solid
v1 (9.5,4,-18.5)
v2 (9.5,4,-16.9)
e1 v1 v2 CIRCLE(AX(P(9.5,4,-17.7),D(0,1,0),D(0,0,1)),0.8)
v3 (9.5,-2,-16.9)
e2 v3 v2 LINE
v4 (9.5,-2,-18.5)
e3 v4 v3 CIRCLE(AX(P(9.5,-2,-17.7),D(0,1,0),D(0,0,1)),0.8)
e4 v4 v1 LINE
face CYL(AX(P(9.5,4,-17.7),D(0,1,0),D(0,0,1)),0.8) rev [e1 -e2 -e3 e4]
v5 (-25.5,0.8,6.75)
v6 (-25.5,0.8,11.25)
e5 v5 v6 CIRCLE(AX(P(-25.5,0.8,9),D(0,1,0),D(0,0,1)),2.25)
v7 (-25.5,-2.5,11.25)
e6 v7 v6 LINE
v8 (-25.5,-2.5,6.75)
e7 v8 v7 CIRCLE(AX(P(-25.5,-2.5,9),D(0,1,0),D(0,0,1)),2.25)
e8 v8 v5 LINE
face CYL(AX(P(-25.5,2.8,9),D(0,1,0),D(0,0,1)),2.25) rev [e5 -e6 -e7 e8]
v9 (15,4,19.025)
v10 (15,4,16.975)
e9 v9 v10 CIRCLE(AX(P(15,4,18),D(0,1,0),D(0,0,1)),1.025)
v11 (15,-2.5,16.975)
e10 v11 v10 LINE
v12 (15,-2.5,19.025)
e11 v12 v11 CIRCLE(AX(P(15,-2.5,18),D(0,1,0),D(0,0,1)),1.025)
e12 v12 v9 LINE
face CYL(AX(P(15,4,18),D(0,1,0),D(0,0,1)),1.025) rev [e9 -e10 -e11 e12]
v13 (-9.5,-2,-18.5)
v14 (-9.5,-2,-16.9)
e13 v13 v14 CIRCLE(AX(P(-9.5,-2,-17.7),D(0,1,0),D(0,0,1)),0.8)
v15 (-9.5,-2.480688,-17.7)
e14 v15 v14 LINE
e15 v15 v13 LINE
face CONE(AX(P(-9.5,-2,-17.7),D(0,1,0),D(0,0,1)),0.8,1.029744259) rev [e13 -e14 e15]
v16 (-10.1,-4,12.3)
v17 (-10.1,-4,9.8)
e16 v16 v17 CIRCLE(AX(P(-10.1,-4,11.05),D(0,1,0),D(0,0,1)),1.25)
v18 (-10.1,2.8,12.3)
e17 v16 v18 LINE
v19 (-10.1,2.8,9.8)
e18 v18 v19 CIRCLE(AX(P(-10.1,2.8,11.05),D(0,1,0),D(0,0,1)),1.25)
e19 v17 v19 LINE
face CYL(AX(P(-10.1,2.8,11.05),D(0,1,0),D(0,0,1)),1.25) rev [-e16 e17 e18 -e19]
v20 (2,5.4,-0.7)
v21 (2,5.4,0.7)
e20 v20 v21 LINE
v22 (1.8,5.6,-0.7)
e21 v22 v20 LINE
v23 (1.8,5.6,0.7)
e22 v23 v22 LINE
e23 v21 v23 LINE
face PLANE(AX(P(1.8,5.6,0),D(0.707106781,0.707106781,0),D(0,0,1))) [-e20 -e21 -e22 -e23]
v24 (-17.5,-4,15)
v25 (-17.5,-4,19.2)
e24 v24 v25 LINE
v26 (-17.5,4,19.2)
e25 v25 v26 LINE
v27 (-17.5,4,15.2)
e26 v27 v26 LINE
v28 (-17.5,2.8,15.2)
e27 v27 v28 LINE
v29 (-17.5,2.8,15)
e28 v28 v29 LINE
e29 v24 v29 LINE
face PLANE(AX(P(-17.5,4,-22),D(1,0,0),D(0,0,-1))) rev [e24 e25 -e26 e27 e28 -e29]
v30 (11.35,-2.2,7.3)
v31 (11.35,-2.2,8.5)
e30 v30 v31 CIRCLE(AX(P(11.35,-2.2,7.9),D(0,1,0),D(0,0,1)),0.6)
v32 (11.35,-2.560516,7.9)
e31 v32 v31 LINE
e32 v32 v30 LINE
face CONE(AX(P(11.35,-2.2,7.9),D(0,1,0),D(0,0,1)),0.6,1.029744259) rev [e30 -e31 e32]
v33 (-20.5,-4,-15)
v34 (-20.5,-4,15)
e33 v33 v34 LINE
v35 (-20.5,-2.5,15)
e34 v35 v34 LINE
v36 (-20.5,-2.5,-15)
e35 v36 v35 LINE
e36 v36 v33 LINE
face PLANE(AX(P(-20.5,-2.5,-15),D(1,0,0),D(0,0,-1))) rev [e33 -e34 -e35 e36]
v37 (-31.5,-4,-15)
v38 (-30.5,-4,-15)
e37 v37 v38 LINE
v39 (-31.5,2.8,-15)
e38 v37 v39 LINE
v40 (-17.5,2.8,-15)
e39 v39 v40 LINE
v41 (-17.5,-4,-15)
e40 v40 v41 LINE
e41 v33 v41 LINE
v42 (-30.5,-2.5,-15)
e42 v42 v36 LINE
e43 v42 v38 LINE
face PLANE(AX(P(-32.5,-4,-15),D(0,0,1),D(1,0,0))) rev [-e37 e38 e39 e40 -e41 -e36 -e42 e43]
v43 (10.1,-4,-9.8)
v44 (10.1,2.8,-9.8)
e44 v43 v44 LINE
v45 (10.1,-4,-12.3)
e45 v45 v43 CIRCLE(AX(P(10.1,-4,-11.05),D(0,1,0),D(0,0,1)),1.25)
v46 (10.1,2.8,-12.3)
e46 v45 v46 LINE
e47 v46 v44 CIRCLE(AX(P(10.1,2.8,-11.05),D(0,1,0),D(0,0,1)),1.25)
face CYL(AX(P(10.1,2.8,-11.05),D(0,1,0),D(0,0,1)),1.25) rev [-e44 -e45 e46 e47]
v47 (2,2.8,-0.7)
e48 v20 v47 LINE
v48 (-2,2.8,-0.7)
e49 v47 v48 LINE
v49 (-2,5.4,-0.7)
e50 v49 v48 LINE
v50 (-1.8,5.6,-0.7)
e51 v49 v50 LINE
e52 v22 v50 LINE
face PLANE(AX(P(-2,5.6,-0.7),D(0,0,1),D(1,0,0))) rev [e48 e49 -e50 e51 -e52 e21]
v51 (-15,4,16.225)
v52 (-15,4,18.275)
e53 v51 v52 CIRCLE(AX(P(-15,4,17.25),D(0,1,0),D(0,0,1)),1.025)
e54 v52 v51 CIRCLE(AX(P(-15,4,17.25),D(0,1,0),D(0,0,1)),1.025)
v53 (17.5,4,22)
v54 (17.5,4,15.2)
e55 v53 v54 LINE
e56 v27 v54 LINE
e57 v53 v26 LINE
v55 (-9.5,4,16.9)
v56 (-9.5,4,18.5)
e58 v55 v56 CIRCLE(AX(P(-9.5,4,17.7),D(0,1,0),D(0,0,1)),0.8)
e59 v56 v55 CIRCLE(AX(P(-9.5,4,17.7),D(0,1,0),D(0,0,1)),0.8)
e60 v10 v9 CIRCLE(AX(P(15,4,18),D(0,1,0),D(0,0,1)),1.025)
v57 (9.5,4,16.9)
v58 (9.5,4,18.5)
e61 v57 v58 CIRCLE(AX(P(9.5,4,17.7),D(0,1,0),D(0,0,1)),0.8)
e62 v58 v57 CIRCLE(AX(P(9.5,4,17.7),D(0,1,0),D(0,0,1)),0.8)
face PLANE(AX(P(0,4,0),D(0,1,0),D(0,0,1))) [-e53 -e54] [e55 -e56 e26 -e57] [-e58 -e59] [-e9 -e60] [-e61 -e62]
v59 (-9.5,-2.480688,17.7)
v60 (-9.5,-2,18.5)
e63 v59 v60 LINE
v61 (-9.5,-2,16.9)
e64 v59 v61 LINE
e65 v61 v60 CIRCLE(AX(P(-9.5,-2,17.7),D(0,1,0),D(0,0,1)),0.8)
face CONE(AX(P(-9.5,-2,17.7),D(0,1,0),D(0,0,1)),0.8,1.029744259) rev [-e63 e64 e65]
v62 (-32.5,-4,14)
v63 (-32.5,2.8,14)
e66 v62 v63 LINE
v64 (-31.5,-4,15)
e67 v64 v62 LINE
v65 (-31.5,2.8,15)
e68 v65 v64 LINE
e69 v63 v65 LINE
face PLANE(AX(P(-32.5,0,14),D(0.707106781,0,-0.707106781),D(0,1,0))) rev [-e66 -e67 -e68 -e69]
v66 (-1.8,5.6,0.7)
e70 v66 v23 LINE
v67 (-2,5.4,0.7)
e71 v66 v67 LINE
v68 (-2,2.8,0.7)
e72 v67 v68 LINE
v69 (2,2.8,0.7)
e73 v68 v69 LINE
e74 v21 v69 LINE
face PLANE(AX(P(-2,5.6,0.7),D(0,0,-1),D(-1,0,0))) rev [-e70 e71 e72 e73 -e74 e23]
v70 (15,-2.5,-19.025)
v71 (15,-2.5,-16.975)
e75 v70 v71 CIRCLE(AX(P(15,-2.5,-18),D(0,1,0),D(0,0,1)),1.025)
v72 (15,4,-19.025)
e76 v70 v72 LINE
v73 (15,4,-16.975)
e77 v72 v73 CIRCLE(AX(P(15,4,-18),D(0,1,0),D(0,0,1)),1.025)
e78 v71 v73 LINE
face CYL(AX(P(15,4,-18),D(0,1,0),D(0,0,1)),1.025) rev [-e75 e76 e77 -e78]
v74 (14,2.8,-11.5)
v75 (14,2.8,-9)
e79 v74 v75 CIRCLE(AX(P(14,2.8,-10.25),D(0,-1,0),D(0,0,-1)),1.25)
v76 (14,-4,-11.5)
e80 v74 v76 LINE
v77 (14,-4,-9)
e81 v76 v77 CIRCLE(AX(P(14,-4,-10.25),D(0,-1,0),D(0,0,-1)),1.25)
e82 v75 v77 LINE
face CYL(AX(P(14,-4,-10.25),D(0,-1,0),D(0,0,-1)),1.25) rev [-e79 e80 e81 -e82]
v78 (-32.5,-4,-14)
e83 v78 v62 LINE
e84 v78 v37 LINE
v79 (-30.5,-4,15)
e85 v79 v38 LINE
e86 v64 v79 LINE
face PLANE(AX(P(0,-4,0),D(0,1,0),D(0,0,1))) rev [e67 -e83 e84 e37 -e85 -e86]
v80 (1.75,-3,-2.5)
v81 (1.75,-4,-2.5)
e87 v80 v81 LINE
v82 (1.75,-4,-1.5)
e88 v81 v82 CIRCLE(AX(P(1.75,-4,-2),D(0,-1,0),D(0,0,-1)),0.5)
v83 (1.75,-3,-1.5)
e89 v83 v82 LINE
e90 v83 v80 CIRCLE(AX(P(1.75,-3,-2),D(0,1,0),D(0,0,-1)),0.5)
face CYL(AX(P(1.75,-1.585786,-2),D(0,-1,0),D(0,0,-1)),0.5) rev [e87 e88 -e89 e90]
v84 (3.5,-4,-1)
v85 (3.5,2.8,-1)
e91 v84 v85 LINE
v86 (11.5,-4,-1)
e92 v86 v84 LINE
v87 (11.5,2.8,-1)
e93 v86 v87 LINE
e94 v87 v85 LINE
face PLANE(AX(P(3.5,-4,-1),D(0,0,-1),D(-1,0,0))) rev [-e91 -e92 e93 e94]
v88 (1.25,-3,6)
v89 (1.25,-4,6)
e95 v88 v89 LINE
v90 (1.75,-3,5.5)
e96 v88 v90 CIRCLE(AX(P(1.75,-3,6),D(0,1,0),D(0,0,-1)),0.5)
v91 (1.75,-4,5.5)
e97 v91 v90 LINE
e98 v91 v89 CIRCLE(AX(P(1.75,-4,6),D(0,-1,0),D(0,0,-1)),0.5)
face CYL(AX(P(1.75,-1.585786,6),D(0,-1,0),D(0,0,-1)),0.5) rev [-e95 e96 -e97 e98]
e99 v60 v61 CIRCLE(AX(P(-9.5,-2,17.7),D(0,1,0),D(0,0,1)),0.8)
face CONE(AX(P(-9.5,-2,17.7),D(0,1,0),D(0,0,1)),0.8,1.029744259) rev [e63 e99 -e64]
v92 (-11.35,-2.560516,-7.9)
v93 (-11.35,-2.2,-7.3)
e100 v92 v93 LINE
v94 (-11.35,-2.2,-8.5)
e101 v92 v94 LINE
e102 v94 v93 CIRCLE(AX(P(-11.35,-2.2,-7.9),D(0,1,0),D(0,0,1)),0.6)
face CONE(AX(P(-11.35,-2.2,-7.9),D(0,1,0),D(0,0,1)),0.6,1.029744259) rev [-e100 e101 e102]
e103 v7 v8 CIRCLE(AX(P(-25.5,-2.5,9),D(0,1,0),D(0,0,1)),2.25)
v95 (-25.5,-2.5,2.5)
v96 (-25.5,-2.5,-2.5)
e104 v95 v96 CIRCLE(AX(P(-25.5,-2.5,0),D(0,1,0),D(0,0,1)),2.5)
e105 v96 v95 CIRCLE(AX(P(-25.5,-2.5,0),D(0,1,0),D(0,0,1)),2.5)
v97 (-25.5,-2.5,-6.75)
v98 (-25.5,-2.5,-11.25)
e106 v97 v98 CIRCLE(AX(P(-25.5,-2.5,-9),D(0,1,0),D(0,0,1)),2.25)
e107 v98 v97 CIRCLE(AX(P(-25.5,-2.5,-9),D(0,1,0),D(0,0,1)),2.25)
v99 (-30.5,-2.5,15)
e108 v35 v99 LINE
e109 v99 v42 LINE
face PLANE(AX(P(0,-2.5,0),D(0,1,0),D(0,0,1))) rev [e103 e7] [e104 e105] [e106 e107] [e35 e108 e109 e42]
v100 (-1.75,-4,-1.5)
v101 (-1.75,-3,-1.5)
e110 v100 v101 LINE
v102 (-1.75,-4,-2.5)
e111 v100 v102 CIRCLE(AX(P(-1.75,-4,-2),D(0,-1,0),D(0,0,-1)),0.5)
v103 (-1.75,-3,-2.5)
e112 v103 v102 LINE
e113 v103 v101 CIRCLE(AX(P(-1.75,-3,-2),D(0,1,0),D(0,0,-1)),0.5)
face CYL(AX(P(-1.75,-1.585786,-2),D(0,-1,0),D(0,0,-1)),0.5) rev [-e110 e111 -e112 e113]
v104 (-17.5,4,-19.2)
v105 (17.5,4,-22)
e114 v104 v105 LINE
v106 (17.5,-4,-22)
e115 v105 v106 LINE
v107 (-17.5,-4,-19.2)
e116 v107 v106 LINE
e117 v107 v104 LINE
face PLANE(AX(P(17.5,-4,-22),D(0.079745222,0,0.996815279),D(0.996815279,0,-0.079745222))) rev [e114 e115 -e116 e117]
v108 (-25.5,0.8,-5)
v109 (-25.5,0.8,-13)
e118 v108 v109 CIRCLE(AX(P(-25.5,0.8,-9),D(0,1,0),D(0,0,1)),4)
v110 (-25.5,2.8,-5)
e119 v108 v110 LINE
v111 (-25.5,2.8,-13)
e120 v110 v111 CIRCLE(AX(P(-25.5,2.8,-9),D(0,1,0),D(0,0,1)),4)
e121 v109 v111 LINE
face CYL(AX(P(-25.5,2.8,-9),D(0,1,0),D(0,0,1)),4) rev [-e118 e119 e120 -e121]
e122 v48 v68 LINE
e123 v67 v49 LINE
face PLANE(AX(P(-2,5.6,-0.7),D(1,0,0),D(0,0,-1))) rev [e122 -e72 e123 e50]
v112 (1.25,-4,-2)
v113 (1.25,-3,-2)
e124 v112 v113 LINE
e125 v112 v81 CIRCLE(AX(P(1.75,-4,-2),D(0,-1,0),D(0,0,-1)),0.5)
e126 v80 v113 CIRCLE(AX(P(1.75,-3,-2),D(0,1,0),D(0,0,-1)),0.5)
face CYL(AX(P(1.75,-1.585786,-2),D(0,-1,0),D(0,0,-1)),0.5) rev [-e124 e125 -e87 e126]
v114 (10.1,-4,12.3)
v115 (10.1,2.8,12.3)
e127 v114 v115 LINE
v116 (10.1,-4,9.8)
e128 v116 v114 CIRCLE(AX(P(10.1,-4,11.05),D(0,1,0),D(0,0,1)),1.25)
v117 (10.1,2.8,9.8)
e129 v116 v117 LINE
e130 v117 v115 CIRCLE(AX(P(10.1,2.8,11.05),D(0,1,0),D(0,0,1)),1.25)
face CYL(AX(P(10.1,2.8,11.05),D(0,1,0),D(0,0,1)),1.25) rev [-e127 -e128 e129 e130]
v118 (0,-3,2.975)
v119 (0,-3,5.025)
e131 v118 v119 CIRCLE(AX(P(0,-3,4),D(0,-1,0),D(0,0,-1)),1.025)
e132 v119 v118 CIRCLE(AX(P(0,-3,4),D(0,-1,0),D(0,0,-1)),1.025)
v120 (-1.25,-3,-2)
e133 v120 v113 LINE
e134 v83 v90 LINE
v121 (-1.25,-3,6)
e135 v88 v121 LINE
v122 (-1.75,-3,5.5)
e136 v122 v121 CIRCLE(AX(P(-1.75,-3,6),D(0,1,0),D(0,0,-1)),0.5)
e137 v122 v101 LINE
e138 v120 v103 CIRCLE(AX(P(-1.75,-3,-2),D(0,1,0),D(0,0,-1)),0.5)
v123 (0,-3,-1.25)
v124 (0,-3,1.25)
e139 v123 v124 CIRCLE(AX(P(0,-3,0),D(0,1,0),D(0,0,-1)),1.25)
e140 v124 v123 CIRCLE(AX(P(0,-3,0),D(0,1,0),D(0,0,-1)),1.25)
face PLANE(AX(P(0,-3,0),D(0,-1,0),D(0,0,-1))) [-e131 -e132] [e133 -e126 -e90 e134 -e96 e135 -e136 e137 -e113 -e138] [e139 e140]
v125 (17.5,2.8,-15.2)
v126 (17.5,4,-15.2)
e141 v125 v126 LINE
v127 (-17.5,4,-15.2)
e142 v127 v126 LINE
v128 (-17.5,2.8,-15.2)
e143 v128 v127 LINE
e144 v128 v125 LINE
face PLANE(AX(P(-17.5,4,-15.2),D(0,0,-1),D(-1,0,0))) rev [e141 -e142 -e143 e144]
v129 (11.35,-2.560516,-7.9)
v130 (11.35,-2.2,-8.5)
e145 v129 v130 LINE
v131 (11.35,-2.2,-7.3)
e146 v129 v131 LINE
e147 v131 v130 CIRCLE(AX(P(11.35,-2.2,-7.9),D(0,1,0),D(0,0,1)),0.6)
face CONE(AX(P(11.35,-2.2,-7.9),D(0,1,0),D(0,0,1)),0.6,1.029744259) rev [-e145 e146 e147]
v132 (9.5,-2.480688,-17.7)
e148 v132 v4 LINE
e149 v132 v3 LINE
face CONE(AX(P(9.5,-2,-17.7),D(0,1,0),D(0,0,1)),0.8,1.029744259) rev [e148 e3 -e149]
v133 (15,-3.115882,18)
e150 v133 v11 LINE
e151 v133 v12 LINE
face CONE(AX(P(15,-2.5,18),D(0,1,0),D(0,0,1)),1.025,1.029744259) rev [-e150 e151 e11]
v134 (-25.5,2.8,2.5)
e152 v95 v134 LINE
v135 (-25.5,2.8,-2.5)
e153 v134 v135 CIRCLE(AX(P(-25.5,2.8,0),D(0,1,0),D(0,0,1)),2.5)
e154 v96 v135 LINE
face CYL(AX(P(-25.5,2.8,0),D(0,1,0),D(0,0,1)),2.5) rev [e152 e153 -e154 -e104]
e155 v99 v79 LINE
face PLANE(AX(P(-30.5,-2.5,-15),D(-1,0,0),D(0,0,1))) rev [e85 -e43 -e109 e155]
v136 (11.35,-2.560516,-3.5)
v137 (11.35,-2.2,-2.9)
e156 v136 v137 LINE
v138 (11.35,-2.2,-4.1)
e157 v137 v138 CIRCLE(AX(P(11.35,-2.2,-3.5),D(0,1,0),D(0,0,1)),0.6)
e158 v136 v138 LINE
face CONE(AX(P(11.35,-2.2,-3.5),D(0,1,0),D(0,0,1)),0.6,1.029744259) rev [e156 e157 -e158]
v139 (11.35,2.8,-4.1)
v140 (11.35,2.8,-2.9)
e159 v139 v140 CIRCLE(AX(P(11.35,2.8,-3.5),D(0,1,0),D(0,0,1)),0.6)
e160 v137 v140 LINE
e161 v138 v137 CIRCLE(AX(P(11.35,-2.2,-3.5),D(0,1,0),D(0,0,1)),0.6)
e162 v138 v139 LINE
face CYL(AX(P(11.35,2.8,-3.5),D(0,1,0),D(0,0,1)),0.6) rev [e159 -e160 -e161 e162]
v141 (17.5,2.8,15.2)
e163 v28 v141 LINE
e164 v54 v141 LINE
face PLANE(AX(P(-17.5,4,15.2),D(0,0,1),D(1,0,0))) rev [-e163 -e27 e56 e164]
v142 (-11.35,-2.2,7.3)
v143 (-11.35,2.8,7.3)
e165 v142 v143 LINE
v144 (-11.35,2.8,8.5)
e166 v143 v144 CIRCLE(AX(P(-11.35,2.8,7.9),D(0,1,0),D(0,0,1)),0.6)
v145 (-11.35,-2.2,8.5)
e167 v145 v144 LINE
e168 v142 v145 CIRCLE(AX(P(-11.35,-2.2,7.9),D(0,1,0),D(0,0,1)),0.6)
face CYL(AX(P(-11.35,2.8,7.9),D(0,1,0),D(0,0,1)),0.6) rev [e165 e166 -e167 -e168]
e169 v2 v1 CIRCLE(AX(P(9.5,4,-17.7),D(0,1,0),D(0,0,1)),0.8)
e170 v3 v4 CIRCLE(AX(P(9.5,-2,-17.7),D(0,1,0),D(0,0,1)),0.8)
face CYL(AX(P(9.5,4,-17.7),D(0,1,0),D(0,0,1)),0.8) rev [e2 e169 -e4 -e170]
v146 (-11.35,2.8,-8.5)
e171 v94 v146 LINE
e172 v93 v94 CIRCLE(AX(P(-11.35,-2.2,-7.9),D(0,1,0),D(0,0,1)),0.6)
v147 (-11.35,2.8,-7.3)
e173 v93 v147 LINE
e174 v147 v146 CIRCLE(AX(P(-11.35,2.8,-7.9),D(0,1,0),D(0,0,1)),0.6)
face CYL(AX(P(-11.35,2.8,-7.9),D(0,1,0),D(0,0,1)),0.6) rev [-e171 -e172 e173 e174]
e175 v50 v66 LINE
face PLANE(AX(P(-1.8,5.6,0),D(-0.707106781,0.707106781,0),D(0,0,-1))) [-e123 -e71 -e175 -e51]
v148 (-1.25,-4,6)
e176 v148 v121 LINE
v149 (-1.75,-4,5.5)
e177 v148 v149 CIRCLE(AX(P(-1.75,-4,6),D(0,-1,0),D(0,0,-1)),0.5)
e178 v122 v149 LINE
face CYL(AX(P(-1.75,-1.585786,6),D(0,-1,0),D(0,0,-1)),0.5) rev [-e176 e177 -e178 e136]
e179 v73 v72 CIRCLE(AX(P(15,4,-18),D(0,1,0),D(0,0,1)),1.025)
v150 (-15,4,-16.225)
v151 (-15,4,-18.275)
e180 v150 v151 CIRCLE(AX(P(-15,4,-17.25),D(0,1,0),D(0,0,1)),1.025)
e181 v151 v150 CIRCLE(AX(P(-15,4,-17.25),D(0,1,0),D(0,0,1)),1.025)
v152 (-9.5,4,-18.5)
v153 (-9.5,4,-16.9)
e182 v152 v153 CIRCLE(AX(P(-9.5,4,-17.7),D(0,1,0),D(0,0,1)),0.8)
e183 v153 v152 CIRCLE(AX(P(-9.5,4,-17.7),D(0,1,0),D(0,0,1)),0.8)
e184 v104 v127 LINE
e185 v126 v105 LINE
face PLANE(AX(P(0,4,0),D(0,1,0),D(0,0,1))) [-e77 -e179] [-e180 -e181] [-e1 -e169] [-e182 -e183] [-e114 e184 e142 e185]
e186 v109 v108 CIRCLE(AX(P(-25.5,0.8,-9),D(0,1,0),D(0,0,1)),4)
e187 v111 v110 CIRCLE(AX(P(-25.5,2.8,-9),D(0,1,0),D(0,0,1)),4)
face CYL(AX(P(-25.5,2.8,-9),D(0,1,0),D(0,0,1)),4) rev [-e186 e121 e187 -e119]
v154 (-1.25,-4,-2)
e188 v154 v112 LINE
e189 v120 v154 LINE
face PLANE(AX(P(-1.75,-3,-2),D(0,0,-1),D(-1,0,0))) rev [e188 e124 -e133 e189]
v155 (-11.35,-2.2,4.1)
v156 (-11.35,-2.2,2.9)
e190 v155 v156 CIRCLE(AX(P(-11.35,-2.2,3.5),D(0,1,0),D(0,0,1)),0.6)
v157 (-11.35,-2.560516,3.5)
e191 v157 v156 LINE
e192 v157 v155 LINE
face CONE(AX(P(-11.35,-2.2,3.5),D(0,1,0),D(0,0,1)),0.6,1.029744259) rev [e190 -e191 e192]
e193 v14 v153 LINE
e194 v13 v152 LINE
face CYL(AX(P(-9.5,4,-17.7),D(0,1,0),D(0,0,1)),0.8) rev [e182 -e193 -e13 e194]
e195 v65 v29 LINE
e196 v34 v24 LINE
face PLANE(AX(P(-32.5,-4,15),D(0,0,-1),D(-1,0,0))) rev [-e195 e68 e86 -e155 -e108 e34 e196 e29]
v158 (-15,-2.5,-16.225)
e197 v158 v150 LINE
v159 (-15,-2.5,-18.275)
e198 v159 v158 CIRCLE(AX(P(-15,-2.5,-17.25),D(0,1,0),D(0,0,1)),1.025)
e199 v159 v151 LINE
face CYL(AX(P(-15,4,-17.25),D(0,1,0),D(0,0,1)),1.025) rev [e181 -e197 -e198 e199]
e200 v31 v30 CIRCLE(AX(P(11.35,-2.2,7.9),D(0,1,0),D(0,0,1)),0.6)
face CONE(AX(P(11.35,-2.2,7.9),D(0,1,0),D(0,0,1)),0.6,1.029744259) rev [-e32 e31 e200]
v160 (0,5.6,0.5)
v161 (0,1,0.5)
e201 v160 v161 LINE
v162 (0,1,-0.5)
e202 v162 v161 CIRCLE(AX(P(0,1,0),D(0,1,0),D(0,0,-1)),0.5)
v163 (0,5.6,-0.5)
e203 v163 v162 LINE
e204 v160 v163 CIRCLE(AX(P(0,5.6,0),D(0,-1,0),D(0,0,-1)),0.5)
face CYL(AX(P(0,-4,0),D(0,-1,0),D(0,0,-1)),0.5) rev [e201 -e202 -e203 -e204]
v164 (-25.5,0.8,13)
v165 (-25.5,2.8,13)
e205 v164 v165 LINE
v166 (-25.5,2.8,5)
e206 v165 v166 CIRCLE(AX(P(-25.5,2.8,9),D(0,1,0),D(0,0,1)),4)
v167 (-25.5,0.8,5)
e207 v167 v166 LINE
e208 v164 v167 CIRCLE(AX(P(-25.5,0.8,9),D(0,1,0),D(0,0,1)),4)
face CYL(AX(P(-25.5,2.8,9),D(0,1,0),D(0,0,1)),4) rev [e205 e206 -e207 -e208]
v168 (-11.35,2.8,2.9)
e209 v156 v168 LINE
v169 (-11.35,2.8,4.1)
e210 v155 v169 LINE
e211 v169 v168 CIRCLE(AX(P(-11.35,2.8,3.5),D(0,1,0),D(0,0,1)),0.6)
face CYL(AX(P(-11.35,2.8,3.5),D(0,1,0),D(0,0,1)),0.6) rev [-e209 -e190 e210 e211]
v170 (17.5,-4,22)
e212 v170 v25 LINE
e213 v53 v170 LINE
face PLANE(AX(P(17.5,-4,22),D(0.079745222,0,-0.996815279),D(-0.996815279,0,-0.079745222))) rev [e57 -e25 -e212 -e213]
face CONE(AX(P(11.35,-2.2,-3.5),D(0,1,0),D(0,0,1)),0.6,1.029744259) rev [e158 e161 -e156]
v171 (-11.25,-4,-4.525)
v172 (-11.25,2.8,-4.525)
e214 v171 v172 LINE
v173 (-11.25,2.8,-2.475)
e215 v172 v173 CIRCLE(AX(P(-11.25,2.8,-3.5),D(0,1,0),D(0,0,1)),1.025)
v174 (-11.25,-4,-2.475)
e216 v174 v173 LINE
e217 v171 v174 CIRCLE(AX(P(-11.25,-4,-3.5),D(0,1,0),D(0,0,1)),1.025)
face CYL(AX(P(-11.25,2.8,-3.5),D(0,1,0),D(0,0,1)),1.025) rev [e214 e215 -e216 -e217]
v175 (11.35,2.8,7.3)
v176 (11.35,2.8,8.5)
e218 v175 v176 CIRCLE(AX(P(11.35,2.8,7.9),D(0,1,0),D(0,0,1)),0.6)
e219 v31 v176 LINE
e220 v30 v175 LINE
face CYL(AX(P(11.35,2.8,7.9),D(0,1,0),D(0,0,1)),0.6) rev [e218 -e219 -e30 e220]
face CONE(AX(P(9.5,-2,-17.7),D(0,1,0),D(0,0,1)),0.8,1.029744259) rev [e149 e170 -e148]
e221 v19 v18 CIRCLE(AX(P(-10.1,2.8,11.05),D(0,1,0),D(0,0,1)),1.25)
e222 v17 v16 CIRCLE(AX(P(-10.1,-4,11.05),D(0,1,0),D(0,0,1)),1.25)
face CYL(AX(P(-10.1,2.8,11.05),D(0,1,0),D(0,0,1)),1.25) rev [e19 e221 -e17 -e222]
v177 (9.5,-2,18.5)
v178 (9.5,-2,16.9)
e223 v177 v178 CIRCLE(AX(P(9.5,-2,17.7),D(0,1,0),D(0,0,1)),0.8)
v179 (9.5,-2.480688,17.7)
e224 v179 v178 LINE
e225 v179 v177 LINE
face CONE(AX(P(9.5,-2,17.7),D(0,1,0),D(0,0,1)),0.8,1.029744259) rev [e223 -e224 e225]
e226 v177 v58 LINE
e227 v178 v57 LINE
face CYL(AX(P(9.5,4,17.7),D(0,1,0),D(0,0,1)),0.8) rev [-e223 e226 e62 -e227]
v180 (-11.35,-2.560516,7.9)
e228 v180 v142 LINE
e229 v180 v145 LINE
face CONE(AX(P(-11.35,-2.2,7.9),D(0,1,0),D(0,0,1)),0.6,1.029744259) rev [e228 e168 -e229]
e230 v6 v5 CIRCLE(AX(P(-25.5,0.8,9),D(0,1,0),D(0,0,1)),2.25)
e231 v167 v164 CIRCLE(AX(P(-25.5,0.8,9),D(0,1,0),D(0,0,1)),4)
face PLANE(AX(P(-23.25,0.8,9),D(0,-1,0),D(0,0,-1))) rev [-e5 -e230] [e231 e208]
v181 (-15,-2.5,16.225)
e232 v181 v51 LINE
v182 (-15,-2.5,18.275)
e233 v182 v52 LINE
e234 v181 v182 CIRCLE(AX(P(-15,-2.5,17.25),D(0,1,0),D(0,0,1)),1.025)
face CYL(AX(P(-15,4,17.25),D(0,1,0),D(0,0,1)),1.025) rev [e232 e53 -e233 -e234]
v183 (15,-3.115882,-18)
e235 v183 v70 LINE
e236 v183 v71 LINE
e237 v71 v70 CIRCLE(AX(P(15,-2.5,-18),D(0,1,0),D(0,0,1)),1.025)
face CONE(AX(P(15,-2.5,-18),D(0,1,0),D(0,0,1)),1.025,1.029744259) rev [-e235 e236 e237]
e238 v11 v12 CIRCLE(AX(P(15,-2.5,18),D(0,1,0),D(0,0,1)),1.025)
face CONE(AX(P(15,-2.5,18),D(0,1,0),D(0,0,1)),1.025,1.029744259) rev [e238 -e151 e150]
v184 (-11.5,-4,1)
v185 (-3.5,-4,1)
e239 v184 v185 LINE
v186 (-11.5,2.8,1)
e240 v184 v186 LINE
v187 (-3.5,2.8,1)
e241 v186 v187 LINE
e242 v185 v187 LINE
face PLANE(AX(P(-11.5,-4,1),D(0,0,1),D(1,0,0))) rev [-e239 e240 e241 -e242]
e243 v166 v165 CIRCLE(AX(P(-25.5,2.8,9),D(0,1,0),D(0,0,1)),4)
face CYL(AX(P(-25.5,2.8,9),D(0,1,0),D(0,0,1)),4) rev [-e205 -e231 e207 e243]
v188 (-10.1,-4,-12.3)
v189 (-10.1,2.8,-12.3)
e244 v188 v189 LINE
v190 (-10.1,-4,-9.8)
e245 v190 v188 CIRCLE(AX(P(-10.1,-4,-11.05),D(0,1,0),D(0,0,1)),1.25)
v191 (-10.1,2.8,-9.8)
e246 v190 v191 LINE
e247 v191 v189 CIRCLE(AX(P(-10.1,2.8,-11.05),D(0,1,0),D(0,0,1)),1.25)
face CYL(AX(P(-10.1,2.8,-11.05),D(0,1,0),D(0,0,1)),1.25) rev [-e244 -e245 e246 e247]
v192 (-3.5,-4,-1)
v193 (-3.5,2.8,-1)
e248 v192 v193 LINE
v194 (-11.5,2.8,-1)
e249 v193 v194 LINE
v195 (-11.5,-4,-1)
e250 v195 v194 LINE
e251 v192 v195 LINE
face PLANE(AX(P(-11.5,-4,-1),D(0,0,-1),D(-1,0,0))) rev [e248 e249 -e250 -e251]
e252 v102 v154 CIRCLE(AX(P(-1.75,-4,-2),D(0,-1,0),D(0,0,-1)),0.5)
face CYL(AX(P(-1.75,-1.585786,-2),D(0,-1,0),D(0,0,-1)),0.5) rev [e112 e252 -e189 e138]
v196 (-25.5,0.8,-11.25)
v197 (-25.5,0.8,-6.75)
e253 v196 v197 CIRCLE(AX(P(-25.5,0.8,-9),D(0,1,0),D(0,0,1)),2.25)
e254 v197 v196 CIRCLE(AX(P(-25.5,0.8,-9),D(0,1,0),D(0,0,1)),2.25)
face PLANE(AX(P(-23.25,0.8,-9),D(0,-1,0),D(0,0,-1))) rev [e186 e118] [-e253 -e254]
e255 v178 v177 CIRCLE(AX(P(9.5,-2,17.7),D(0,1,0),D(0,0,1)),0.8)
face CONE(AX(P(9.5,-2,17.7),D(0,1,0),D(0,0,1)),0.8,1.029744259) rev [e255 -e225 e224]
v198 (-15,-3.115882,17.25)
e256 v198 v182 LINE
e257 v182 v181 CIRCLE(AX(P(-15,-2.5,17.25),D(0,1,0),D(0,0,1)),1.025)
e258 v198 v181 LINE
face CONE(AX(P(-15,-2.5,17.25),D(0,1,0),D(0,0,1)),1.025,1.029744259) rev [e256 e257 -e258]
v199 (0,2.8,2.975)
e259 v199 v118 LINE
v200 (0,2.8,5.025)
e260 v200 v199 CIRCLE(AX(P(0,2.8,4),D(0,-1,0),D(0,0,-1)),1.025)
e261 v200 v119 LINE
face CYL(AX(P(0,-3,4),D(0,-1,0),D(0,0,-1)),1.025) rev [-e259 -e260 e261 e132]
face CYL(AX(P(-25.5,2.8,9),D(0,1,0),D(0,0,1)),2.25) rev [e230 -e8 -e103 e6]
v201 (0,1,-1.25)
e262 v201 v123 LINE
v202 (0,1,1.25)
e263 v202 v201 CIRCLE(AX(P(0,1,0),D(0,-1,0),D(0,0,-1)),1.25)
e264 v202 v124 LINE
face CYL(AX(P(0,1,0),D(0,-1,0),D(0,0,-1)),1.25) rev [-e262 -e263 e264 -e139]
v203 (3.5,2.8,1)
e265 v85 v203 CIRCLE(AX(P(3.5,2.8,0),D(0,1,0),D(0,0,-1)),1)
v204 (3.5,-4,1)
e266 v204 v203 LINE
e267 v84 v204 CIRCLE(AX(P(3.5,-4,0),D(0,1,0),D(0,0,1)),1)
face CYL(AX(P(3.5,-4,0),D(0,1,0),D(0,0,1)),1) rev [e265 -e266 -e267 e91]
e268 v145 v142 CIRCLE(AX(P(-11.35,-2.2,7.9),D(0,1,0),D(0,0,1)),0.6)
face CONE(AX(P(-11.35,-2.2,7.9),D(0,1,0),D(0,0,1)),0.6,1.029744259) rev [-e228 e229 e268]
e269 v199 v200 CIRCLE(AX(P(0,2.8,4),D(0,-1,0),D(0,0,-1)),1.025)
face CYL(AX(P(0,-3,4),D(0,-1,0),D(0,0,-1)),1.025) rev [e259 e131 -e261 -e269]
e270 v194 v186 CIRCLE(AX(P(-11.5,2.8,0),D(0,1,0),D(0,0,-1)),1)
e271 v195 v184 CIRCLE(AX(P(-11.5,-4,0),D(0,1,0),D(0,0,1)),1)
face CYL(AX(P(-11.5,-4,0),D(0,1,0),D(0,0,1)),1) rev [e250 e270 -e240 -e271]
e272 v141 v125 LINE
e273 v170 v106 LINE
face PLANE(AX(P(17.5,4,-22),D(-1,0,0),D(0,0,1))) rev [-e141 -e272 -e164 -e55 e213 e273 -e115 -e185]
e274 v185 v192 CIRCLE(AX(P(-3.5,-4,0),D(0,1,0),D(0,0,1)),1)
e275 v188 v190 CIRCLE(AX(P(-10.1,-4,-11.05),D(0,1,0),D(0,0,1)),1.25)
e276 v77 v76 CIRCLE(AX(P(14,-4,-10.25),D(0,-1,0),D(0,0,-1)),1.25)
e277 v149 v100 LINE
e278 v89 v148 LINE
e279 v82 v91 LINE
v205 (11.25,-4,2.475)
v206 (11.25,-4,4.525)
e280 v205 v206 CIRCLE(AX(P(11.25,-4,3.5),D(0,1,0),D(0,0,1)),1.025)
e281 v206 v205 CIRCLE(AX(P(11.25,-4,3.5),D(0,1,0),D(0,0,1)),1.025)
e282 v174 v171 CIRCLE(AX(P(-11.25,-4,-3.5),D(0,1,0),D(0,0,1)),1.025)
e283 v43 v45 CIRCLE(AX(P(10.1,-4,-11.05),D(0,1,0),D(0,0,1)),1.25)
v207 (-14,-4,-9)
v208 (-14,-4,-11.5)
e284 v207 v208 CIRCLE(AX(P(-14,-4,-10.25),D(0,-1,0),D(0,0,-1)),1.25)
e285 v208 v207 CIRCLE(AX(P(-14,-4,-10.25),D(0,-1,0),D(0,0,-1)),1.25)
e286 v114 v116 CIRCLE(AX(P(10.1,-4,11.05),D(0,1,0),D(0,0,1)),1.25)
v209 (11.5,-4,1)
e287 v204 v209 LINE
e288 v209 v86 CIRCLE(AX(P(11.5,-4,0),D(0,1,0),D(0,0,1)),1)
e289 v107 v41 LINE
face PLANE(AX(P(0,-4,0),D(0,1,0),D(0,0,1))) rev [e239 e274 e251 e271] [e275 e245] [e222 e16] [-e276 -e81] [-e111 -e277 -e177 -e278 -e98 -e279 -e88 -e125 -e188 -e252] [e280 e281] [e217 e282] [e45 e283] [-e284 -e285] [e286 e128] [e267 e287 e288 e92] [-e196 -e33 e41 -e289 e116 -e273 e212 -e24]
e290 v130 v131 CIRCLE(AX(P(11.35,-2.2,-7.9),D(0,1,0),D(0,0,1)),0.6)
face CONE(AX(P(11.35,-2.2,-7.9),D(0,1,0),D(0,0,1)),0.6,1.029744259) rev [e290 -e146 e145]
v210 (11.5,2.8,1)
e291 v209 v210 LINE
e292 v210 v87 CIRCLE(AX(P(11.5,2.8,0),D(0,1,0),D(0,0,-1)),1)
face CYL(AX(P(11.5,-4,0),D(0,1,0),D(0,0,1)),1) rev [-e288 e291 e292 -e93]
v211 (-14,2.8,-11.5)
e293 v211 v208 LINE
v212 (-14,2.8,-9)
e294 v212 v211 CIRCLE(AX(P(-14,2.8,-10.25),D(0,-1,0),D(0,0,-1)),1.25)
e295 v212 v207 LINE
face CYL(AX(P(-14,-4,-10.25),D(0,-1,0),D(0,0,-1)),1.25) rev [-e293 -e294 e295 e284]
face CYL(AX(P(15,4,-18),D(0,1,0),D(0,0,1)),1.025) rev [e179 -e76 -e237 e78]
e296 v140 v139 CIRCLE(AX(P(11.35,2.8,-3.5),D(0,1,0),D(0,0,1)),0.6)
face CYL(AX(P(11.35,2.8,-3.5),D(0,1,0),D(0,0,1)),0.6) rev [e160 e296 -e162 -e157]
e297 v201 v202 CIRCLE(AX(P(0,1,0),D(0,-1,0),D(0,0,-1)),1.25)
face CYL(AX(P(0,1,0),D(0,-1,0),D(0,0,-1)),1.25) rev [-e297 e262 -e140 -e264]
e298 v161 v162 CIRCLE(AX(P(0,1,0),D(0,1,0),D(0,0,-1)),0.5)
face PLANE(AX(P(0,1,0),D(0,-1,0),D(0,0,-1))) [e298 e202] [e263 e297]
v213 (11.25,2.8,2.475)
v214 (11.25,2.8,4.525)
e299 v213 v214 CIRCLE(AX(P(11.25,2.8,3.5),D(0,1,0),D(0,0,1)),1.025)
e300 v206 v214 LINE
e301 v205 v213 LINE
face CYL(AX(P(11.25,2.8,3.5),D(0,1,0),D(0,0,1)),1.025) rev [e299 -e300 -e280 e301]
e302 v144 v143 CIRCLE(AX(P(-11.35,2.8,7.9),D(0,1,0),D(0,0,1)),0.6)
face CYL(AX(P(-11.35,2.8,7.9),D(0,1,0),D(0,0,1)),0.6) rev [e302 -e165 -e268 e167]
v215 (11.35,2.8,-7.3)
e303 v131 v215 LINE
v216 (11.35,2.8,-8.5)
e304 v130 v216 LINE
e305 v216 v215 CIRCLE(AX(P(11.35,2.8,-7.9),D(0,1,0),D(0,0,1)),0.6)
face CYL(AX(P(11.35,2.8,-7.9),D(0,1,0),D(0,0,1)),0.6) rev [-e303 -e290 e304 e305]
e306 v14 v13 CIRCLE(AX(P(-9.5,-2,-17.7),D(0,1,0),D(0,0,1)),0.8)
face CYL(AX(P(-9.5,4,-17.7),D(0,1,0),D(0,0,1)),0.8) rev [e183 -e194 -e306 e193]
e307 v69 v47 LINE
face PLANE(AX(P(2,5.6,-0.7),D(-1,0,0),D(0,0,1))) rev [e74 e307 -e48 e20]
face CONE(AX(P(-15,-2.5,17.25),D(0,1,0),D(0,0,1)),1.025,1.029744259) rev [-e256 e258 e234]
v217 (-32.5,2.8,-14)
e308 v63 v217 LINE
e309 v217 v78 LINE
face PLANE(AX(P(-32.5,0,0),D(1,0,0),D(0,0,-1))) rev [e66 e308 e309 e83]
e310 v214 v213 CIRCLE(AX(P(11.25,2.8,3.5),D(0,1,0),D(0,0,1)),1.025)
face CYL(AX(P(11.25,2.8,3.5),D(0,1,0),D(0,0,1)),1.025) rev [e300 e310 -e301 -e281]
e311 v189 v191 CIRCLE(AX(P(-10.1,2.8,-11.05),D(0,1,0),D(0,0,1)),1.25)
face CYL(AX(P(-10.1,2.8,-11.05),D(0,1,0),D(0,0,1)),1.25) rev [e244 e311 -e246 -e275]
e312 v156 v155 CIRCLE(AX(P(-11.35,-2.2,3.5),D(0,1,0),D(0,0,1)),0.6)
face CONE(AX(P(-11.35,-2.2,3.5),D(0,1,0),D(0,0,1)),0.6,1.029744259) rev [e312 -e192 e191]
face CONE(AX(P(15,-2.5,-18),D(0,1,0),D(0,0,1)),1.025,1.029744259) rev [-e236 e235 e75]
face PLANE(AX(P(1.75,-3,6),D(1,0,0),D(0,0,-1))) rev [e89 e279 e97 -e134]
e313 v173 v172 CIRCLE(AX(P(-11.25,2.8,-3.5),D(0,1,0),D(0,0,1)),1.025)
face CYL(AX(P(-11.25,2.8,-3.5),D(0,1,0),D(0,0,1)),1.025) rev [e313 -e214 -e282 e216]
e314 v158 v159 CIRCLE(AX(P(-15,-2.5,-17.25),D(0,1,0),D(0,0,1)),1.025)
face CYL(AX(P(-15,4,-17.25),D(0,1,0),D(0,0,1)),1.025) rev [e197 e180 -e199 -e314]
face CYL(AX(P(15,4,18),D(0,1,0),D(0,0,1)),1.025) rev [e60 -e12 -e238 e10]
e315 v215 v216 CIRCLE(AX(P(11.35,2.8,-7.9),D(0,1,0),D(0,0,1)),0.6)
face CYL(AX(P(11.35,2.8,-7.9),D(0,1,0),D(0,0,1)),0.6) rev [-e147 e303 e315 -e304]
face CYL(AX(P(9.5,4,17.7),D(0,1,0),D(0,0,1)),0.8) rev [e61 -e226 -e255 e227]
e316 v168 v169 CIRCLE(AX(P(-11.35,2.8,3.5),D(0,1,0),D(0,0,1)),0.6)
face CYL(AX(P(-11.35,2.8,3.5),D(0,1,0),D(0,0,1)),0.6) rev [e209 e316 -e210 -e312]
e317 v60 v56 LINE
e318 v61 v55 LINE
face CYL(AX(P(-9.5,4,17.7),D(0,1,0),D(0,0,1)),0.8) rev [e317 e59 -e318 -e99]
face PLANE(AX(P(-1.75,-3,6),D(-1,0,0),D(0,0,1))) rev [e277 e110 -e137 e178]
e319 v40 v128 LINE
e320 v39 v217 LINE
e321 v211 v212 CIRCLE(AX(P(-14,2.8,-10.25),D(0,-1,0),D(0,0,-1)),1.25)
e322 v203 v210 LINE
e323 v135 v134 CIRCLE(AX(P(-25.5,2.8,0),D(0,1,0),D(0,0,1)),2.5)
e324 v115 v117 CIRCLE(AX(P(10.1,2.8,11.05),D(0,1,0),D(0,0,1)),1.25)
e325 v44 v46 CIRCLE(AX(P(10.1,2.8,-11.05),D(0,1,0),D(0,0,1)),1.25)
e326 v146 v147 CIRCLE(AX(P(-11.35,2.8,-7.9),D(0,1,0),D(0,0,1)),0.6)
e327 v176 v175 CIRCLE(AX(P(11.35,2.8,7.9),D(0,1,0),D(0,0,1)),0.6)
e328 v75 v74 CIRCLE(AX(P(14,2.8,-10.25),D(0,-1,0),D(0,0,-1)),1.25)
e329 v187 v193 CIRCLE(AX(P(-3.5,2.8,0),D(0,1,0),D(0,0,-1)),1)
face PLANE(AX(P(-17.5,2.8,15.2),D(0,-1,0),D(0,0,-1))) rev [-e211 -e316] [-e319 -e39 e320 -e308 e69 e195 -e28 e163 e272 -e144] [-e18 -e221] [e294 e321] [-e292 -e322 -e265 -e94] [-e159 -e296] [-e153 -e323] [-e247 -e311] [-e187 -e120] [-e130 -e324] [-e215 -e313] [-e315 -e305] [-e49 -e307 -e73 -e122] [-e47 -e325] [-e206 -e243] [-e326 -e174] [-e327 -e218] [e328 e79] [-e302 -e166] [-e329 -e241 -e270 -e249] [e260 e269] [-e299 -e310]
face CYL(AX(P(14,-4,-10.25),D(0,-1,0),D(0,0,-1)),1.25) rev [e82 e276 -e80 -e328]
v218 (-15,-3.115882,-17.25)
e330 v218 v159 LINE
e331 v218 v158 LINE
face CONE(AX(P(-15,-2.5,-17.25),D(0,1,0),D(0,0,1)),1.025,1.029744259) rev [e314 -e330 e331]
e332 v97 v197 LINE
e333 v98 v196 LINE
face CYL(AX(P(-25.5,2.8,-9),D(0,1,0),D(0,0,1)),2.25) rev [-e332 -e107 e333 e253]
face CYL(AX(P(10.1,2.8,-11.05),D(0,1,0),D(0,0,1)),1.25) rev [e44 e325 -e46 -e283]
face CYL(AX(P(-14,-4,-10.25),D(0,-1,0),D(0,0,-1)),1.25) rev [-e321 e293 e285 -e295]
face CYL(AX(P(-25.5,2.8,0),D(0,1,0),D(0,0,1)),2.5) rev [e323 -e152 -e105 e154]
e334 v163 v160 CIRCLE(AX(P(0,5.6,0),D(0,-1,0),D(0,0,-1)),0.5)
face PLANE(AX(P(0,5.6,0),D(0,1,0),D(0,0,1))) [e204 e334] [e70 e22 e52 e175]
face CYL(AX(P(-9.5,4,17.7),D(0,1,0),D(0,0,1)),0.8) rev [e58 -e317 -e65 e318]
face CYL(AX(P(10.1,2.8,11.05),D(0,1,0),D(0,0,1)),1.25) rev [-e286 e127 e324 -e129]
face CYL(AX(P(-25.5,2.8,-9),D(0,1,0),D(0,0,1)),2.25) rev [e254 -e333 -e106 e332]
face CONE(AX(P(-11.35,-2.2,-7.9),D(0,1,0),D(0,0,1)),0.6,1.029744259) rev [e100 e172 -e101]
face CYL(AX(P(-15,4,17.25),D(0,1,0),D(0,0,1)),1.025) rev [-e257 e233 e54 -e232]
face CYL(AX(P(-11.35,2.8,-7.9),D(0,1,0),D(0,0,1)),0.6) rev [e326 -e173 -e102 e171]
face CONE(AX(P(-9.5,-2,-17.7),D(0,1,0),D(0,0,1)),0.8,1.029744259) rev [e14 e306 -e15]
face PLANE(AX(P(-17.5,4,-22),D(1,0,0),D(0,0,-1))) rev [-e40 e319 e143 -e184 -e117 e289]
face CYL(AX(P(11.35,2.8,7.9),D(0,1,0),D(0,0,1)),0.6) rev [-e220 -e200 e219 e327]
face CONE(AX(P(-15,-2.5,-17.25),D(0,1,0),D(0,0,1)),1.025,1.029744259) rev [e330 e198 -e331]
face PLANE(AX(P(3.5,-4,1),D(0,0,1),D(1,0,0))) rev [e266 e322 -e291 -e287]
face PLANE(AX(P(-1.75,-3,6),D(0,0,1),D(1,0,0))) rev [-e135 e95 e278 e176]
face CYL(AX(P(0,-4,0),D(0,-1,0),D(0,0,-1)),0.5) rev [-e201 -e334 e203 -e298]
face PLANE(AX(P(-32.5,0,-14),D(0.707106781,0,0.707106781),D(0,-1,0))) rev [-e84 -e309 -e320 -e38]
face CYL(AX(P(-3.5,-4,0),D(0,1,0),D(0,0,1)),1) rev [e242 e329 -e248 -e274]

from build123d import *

# Parameters (mm, degrees)
SKETCH1_W                                            = 35
SKETCH1_H                                            = 44
BOSS_EXTRUDE1_DEPTH                                  = 4
CUT_EXTRUDE2_DEPTH                                   = 30.227555491
SKETCH15_W                                           = 30.4
SKETCH15_H                                           = 1.2
CUT_EXTRUDE6_DEPTH                                   = 42.533119315
SKETCH4_W                                            = 4
SKETCH4_H                                            = 1.4
BOSS_EXTRUDE2_DEPTH                                  = 2.8
CHAMFER1_SIZE                                        = 0.2
F_1_2_1_2_DIAMETER_HOLE1_D                           = 1
SKETCH7_R                                            = 1.25
CUT_EXTRUDE3_DEPTH                                   = 5
M3_TAPPED_HOLE1_D                                    = 2.5
SKETCH11_W                                           = 3.5
SKETCH11_H                                           = 8
CUT_EXTRUDE4_DEPTH                                   = 1
SKETCH12_R                                           = 0.5
CUT_EXTRUDE5_DEPTH                                   = 1
M2_5_TAPPED_HOLE1_D                                  = 2.05
F_1_2_1_2_DIAMETER_HOLE2_D                           = 1.2
F_1_2_1_2_DIAMETER_HOLE2_DEPTH                       = 5
F_1_2_1_2_DIAMETER_HOLE2_TIP                         = 0.360516371
M2_5_TAPPED_HOLE2_D                                  = 2.05
M3_TAPPED_HOLE2_D                                    = 2.5
CUT_EXTRUDE7_DEPTH                                   = 30.227555491
M2_5_TAPPED_HOLE3_D                                  = 2.05
M2_5_TAPPED_HOLE3_DEPTH                              = 6.5
M2_5_TAPPED_HOLE3_TIP                                = 0.615882135
M2_TAPPED_HOLE1_D                                    = 1.6
M2_TAPPED_HOLE1_DEPTH                                = 6
M2_TAPPED_HOLE1_TIP                                  = 0.480688495
SKETCH29_W                                           = 30
SKETCH29_H                                           = 6.8
BOSS_EXTRUDE3_DEPTH                                  = 15
SKETCH30_W                                           = 10
SKETCH30_H                                           = 30
CUT_EXTRUDE8_DEPTH                                   = 1.5
HOLE_SIZE_PER_SOCKET_HEAD_CAP_SCREW_TYPE_D           = 4.5
HOLE_SIZE_PER_SOCKET_HEAD_CAP_SCREW_TYPE_CBORE_D     = 8
HOLE_SIZE_PER_SOCKET_HEAD_CAP_SCREW_TYPE_CBORE_DEPTH = 2
CHAMFER3_SIZE                                        = 1
F_5_0_5_DIAMETER_HOLE1_D                             = 5


with BuildPart() as part:
    # Sketch1 → Boss-Extrude1 (new, symmetric)
    with BuildSketch(Plane(origin=(0, 0, 0), x_dir=(1, 0, 0), z_dir=(0, 1, 0))):
        Rectangle(SKETCH1_W, SKETCH1_H)
    extrude(amount=BOSS_EXTRUDE1_DEPTH, both=True)

    # Sketch3 → Cut-Extrude2 (cut, through all)
    with BuildSketch(Plane(origin=(0, 4, 0), x_dir=(1, 0, 0), z_dir=(0, 1, 0))):
        with BuildLine():
            Line((-11.5, 1), (-3.5, 1))
            ThreePointArc((-3.5, 1), (-2.5, 0), (-3.5, -1))
            Line((-3.5, -1), (-11.5, -1))
            ThreePointArc((-11.5, -1), (-12.5, 0), (-11.5, 1))
        make_face()
        with BuildLine():
            Line((3.5, 1), (11.5, 1))
            ThreePointArc((11.5, 1), (12.5, 0), (11.5, -1))
            Line((11.5, -1), (3.5, -1))
            ThreePointArc((3.5, -1), (2.5, 0), (3.5, 1))
        make_face()
    extrude(amount=-CUT_EXTRUDE2_DEPTH, mode=Mode.SUBTRACT)

    # Sketch15 → Cut-Extrude6 (cut, through all)
    with BuildSketch(Plane(origin=(17.5, 0, 0), x_dir=(0, 0, -1), z_dir=(1, 0, 0))):
        with Locations((0, 3.4)):
            Rectangle(SKETCH15_W, SKETCH15_H)
    extrude(amount=-CUT_EXTRUDE6_DEPTH, mode=Mode.SUBTRACT)

    # Sketch4 → Boss-Extrude2 (add)
    with BuildSketch(Plane(origin=(0, 2.8, 0), x_dir=(1, 0, 0), z_dir=(0, 1, 0))):
        Rectangle(SKETCH4_W, SKETCH4_H)
    extrude(amount=BOSS_EXTRUDE2_DEPTH)

    # Chamfer1
    chamfer1_edges = [part.edges().sort_by_distance(p)[0] for p in [
        (2, 5.6, 0),
        (-2, 5.6, 0),
    ]]
    chamfer(chamfer1_edges, length=CHAMFER1_SIZE)

    # Ø1.2 (1.2) Diameter Hole1 (through all)
    with Locations(Plane(origin=(0, -4, 0), x_dir=(-1, 0, 0), z_dir=(0, -1, 0))):
        with Locations((0, 0)):
            Hole(F_1_2_1_2_DIAMETER_HOLE1_D / 2)

    # Sketch7 → Cut-Extrude3 (cut)
    with BuildSketch(Plane.XZ.offset(4)):
        with Locations(Location((0, 0, 0), (0, 0, 270))):
            Circle(SKETCH7_R)
    extrude(amount=-CUT_EXTRUDE3_DEPTH, mode=Mode.SUBTRACT)

    # M3 Tapped Hole1 (through all)
    with Locations(Plane(origin=(0, -4, 0), x_dir=(-1, 0, 0), z_dir=(0, -1, 0))):
        with Locations((14, 10.25), (-14, 10.25)):
            Hole(M3_TAPPED_HOLE1_D / 2)

    # Sketch11 → Cut-Extrude4 (cut)
    with BuildSketch(Plane.XZ.offset(4)):
        with Locations((0, 2)):
            Rectangle(SKETCH11_W, SKETCH11_H)
    extrude(amount=-CUT_EXTRUDE4_DEPTH, mode=Mode.SUBTRACT)

    # Sketch12 → Cut-Extrude5 (cut)
    with BuildSketch(Plane.XZ.offset(4)):
        with Locations((-1.75, 6)):
            Circle(SKETCH12_R)
        with Locations((1.75, 6)):
            Circle(SKETCH12_R)
        with Locations((-1.75, -2)):
            Circle(SKETCH12_R)
        with Locations((1.75, -2)):
            Circle(SKETCH12_R)
    extrude(amount=-CUT_EXTRUDE5_DEPTH, mode=Mode.SUBTRACT)

    # M2.5 Tapped Hole1 (through all)
    with Locations(Plane(origin=(0, -3, 0), x_dir=(-1, 0, 0), z_dir=(0, -1, 0))):
        with Locations((0, -4)):
            Hole(M2_5_TAPPED_HOLE1_D / 2)

    # Ø1.2 (1.2) Diameter Hole2
    with Locations(Plane(origin=(0, 2.8, 0), x_dir=(1, 0, 0), z_dir=(0, 1, 0))):
        with Locations((-11.35, 7.9), (11.35, 7.9), (-11.35, -3.5), (11.35, 3.5), (11.35, -7.9), (-11.35, -7.9)):
            Hole(F_1_2_1_2_DIAMETER_HOLE2_D / 2, depth=F_1_2_1_2_DIAMETER_HOLE2_DEPTH)
            with Locations((0, 0, -(F_1_2_1_2_DIAMETER_HOLE2_DEPTH + F_1_2_1_2_DIAMETER_HOLE2_TIP / 2))):  # 118° drill point
                Cone(0, F_1_2_1_2_DIAMETER_HOLE2_D / 2, F_1_2_1_2_DIAMETER_HOLE2_TIP, mode=Mode.SUBTRACT)

    # M2.5 Tapped Hole2 (through all)
    with Locations(Plane(origin=(0, 2.8, 0), x_dir=(1, 0, 0), z_dir=(0, 1, 0))):
        with Locations((-11.25, 3.5), (11.25, -3.5)):
            Hole(M2_5_TAPPED_HOLE2_D / 2)

    # M3 Tapped Hole2 (through all)
    with Locations(Plane(origin=(0, 2.8, 0), x_dir=(1, 0, 0), z_dir=(0, 1, 0))):
        with Locations((-10.1, 11.05), (10.1, 11.05), (-10.1, -11.05), (10.1, -11.05)):
            Hole(M3_TAPPED_HOLE2_D / 2)

    # Sketch22 → Cut-Extrude7 (cut, through all)
    with BuildSketch(Plane(origin=(0, 4, 0), x_dir=(1, 0, 0), z_dir=(0, 1, 0))):
        Polygon((-17.5, -19.2), (-17.5, -22), (17.5, -22), align=None)
        Polygon((-17.5, 19.2), (-17.5, 22), (17.5, 22), align=None)
    extrude(amount=-CUT_EXTRUDE7_DEPTH, mode=Mode.SUBTRACT)

    # M2.5 Tapped Hole3
    with Locations(Plane(origin=(0, 4, 0), x_dir=(1, 0, 0), z_dir=(0, 1, 0))):
        with Locations((-15, -17.25), (-15, 17.25), (15, 18), (15, -18)):
            Hole(M2_5_TAPPED_HOLE3_D / 2, depth=M2_5_TAPPED_HOLE3_DEPTH)
            with Locations((0, 0, -(M2_5_TAPPED_HOLE3_DEPTH + M2_5_TAPPED_HOLE3_TIP / 2))):  # 118° drill point
                Cone(0, M2_5_TAPPED_HOLE3_D / 2, M2_5_TAPPED_HOLE3_TIP, mode=Mode.SUBTRACT)

    # M2 Tapped Hole1
    with Locations(Plane(origin=(0, 4, 0), x_dir=(1, 0, 0), z_dir=(0, 1, 0))):
        with Locations((-9.5, 17.7), (9.5, 17.7), (9.5, -17.7), (-9.5, -17.7)):
            Hole(M2_TAPPED_HOLE1_D / 2, depth=M2_TAPPED_HOLE1_DEPTH)
            with Locations((0, 0, -(M2_TAPPED_HOLE1_DEPTH + M2_TAPPED_HOLE1_TIP / 2))):  # 118° drill point
                Cone(0, M2_TAPPED_HOLE1_D / 2, M2_TAPPED_HOLE1_TIP, mode=Mode.SUBTRACT)

    # Sketch29 → Boss-Extrude3 (add)
    with BuildSketch(Plane.ZY.offset(17.5)):
        with Locations((0, -0.6)):
            Rectangle(SKETCH29_W, SKETCH29_H)
    extrude(amount=BOSS_EXTRUDE3_DEPTH)

    # Sketch30 → Cut-Extrude8 (cut)
    with BuildSketch(Plane.XZ.offset(4)):
        with Locations((-25.5, 0)):
            Rectangle(SKETCH30_W, SKETCH30_H)
    extrude(amount=-CUT_EXTRUDE8_DEPTH, mode=Mode.SUBTRACT)

    # Hole size per socket head cap screw type1 (through all)
    with Locations(Plane(origin=(0, 2.8, 0), x_dir=(1, 0, 0), z_dir=(0, 1, 0))):
        with Locations((-25.5, 9), (-25.5, -9)):
            CounterBoreHole(HOLE_SIZE_PER_SOCKET_HEAD_CAP_SCREW_TYPE_D / 2, HOLE_SIZE_PER_SOCKET_HEAD_CAP_SCREW_TYPE_CBORE_D / 2, HOLE_SIZE_PER_SOCKET_HEAD_CAP_SCREW_TYPE_CBORE_DEPTH)

    # Chamfer3
    chamfer3_edges = [part.edges().sort_by_distance(p)[0] for p in [
        (-32.5, -0.6, 15),
        (-32.5, -0.6, -15),
    ]]
    chamfer(chamfer3_edges, length=CHAMFER3_SIZE)

    # Ø5.0 (5) Diameter Hole1 (through all)
    with Locations(Plane(origin=(0, 2.8, 0), x_dir=(1, 0, 0), z_dir=(0, 1, 0))):
        with Locations((-25.5, 0)):
            Hole(F_5_0_5_DIAMETER_HOLE1_D / 2)


solid = part.part
